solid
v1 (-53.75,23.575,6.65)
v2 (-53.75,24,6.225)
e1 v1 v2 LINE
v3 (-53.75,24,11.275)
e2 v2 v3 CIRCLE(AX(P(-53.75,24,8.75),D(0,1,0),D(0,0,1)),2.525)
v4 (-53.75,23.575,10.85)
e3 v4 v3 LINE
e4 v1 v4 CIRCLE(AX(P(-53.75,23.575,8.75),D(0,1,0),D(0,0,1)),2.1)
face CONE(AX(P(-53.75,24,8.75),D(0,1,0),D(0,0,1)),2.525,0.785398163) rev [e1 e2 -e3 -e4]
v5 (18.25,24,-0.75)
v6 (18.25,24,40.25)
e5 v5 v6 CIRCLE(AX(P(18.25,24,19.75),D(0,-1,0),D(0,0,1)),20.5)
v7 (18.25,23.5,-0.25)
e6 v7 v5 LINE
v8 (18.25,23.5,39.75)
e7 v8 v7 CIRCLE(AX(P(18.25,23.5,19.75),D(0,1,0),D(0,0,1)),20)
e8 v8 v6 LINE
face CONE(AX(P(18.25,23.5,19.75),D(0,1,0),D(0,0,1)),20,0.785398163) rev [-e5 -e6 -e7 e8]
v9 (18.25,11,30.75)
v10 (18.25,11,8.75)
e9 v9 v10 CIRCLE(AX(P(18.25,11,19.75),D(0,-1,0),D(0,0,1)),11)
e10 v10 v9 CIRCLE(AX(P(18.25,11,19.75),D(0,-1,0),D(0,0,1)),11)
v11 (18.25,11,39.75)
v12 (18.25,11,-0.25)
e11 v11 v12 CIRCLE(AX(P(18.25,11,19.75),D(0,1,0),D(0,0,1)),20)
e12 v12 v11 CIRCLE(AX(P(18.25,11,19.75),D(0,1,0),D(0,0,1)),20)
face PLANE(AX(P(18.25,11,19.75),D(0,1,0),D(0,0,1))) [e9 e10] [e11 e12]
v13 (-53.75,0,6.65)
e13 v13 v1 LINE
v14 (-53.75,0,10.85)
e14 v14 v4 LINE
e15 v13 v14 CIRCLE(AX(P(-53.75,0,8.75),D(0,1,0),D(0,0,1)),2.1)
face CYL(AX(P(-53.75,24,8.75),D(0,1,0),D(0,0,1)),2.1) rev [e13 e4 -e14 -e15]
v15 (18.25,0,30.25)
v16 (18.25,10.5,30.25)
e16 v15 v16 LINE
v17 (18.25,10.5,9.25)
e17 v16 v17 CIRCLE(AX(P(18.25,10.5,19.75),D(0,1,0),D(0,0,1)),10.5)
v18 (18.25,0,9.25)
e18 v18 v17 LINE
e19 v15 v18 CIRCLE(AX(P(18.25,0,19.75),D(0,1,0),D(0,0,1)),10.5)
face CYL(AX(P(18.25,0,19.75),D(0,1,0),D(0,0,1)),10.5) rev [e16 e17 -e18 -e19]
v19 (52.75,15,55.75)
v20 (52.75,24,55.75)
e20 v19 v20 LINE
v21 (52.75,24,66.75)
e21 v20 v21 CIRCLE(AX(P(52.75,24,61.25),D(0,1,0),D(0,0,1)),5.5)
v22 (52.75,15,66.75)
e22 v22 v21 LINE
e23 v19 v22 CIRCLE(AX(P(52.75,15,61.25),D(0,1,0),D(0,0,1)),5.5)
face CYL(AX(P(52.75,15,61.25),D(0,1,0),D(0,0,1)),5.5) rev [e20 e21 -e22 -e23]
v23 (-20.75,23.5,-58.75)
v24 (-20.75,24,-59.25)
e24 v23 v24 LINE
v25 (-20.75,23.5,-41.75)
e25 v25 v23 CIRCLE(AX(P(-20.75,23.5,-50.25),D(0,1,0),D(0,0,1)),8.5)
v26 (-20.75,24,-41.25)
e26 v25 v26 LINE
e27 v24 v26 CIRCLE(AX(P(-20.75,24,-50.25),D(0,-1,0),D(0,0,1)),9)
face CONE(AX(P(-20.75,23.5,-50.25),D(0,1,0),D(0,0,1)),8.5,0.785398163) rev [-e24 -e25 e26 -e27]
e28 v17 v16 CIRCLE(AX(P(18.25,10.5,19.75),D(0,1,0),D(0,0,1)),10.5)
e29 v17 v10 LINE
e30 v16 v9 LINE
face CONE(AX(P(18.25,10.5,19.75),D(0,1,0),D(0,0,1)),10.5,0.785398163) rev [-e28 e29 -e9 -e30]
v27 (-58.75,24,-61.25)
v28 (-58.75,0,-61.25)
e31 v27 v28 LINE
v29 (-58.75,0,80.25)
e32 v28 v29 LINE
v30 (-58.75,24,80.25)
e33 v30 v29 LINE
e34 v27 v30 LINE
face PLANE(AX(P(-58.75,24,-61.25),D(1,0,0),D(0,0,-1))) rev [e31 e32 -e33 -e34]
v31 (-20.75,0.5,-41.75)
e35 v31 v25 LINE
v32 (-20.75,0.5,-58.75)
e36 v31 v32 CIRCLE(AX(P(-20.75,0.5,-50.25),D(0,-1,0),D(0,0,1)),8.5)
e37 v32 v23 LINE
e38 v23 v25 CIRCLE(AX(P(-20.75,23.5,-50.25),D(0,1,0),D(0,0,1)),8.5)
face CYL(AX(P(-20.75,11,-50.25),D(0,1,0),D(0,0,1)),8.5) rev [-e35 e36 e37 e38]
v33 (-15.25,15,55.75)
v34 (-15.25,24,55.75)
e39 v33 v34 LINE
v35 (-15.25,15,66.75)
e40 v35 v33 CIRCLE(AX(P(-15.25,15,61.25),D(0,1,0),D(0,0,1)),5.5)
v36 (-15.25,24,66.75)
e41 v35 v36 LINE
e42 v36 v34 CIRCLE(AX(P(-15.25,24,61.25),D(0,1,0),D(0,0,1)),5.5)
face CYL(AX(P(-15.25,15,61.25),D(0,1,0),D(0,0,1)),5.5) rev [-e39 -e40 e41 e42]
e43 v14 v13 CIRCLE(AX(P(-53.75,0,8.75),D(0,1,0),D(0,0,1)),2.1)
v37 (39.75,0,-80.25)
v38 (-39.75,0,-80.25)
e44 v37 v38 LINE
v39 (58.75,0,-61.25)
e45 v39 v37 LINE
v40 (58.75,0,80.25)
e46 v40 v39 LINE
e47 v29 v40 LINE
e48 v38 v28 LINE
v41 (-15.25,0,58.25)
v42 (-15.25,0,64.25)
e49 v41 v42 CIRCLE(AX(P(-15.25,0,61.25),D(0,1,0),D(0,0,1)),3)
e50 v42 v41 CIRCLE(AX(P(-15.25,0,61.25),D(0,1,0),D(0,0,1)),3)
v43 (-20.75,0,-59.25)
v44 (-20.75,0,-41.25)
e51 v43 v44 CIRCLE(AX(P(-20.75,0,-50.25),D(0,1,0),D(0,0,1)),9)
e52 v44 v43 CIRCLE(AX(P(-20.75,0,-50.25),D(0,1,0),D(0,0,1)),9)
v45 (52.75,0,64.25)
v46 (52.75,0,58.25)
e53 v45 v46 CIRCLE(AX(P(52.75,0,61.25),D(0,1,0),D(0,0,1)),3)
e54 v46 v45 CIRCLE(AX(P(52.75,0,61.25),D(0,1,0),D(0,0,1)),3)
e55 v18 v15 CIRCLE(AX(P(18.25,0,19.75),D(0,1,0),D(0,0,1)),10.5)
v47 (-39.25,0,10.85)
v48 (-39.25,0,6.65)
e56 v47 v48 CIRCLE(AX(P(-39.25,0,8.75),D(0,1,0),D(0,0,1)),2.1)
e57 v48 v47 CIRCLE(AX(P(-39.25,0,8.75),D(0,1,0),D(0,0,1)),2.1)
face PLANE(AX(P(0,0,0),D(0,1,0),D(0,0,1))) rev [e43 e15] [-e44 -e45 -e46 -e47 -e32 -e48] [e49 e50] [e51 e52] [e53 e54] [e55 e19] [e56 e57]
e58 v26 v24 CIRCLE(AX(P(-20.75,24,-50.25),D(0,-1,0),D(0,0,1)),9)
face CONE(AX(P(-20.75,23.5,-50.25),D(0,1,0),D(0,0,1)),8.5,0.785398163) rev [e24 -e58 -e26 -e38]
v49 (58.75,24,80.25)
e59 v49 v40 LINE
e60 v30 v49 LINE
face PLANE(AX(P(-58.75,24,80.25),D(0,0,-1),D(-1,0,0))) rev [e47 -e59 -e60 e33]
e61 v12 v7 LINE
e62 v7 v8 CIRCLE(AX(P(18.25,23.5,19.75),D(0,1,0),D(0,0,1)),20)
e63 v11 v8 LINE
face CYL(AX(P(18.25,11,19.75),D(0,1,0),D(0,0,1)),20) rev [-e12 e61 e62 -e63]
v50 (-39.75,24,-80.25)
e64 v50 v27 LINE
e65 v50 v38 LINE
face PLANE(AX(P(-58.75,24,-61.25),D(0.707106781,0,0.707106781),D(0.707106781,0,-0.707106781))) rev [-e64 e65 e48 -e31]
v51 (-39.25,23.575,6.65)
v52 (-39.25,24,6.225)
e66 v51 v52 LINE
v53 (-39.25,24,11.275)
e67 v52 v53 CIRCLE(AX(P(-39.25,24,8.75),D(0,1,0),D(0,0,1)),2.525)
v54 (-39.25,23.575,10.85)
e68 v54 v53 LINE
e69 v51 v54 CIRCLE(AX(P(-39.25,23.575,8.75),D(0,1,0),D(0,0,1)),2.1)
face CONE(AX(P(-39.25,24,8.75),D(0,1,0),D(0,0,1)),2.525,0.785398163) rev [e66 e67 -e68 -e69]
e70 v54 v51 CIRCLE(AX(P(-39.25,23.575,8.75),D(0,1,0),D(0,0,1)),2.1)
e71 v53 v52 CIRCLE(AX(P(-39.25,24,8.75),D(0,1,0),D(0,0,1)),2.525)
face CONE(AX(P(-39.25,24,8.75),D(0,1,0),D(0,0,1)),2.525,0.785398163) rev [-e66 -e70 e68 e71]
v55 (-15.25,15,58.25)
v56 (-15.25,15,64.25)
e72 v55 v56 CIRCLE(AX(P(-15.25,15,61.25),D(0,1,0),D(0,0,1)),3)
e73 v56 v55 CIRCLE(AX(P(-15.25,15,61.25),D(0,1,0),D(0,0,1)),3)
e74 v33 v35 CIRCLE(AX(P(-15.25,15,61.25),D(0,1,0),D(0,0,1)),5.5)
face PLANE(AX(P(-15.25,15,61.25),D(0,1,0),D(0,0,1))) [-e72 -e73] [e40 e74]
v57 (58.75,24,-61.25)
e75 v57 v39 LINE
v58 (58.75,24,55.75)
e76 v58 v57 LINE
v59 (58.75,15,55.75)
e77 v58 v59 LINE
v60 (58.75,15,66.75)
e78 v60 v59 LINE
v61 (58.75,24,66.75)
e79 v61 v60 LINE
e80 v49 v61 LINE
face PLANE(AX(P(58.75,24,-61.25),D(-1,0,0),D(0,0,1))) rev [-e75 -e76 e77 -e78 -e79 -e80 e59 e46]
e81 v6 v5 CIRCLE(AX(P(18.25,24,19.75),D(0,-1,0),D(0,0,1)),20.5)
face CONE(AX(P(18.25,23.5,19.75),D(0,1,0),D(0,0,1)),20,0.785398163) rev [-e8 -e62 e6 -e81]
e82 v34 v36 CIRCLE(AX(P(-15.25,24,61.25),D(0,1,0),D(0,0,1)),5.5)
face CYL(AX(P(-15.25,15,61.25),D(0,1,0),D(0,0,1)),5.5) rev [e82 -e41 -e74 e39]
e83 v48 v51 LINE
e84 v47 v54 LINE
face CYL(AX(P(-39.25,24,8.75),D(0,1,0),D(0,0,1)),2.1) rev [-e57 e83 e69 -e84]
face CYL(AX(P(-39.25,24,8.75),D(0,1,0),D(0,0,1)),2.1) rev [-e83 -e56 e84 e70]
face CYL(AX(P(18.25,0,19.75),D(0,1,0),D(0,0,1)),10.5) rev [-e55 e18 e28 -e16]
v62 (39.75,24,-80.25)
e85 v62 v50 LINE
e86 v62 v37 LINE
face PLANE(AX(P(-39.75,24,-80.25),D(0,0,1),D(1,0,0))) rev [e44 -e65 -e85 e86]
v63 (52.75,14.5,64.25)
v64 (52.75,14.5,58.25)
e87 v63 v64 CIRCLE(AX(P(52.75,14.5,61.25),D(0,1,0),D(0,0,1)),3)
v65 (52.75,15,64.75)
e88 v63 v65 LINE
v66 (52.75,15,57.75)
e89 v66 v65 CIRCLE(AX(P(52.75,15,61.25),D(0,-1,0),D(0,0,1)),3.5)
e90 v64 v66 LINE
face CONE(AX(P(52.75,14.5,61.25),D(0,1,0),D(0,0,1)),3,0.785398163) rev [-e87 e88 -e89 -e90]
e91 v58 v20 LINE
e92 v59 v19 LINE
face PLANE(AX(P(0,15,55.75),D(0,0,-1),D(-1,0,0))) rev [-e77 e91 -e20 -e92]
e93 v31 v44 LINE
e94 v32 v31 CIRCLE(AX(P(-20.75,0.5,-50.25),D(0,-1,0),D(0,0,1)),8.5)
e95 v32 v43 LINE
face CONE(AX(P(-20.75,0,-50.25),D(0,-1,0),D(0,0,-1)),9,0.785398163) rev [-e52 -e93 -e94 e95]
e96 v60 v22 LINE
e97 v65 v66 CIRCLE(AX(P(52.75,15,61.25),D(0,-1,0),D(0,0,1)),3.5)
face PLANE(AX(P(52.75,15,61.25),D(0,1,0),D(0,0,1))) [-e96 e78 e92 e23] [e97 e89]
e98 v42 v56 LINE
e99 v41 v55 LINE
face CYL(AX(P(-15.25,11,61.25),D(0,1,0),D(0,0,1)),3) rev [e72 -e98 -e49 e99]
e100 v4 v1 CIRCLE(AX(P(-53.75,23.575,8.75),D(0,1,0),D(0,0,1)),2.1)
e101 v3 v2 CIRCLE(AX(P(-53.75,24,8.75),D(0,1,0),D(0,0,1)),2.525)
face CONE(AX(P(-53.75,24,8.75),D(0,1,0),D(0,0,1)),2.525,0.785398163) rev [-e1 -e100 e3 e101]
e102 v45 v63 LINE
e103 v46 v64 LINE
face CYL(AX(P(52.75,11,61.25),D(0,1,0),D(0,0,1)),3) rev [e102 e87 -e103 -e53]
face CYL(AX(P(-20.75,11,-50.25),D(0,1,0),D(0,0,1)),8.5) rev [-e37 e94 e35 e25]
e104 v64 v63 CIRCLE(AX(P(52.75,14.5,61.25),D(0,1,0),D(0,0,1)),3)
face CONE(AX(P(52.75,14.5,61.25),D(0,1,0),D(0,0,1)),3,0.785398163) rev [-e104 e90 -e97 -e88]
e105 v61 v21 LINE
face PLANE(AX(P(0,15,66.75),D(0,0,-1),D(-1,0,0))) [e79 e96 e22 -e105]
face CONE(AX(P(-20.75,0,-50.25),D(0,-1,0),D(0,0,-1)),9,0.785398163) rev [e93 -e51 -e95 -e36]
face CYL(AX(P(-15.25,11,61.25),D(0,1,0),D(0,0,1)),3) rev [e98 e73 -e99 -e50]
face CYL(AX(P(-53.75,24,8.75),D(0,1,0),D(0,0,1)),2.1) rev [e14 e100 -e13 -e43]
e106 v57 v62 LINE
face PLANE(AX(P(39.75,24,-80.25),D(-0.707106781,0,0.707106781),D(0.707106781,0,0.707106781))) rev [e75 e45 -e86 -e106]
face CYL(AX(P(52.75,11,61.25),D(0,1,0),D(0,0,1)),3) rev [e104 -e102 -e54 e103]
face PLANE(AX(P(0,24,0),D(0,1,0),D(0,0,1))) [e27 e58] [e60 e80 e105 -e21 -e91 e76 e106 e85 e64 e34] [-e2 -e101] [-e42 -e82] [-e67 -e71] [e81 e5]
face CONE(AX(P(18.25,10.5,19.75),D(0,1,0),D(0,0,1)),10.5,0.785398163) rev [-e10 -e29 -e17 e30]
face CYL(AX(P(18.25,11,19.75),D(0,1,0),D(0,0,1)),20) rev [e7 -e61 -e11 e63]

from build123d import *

# Parameters (mm, degrees)
BOSS_EXTRUDE1_DEPTH         = 24
SKETCH_2_2_R                = 8.5
SKETCH_2_2_R_2              = 20
SKETCH_2_2_R_3              = 3
CUT_EXTRUDE1_DEPTH          = 13
SKETCH_2_2_2_R              = 8.5
SKETCH_2_2_2_R_2            = 3
CUT_EXTRUDE2_DEPTH          = 103.311411876
SKETCH3_R                   = 10.5
CUT_EXTRUDE3_DEPTH          = 101.302666964
M5_TAPPED_HOLE1_D           = 4.2
M5_TAPPED_HOLE1_CSINK_D     = 5.05
M5_TAPPED_HOLE1_CSINK_ANGLE = 90
CHAMFER1_SIZE               = 0.5
CUT_EXTRUDE4_START          = -24
SKETCH6_R                   = 5.5
SKETCH6_R_2                 = 3
SKETCH6_W                   = 5.693229178
SKETCH6_H                   = 11
CUT_EXTRUDE4_DEPTH          = 9
CHAMFER2_SIZE               = 0.5


with BuildPart() as part:
    # Sketch1 → Boss-Extrude1 (new body)
    with BuildSketch(Plane(origin=(0, 0, 0), x_dir=(1, 0, 0), z_dir=(0, 1, 0))):
        Polygon((-58.75, 61.25), (-39.75, 80.25), (39.75, 80.25), (58.75, 61.25), (58.75, -80.25), (-58.75, -80.25), align=None)
    extrude(amount=BOSS_EXTRUDE1_DEPTH)

    # Sketch 2_2 → Cut-Extrude1 (cut)
    with BuildSketch(Plane(origin=(0, 24, 0), x_dir=(1, 0, 0), z_dir=(0, 1, 0))):
        with Locations(Location((-20.75, 50.25, 0), (0, 0, 270))):
            Circle(SKETCH_2_2_R)
        with Locations(Location((18.25, -19.75, 0), (0, 0, 270))):
            Circle(SKETCH_2_2_R_2)
        with Locations(Location((52.75, -61.25, 0), (0, 0, 270))):
            Circle(SKETCH_2_2_R_3)
        with Locations(Location((-15.25, -61.25, 0), (0, 0, 270))):
            Circle(SKETCH_2_2_R_3)
    extrude(amount=-CUT_EXTRUDE1_DEPTH, mode=Mode.SUBTRACT)

    # Sketch 2_2 2 → Cut-Extrude2 (cut, through all)
    with BuildSketch(Plane(origin=(0, 24, 0), x_dir=(1, 0, 0), z_dir=(0, 1, 0))):
        with Locations(Location((-20.75, 50.25, 0), (0, 0, 270))):
            Circle(SKETCH_2_2_2_R)
        with Locations(Location((52.75, -61.25, 0), (0, 0, 270))):
            Circle(SKETCH_2_2_2_R_2)
        with Locations(Location((-15.25, -61.25, 0), (0, 0, 270))):
            Circle(SKETCH_2_2_2_R_2)
    extrude(amount=-CUT_EXTRUDE2_DEPTH, mode=Mode.SUBTRACT)

    # Sketch3 → Cut-Extrude3 (cut, through all)
    with BuildSketch(Plane(origin=(0, 11, 0), x_dir=(1, 0, 0), z_dir=(0, 1, 0))):
        with Locations(Location((18.25, -19.75, 0), (0, 0, 270))):
            Circle(SKETCH3_R)
    extrude(amount=-CUT_EXTRUDE3_DEPTH, mode=Mode.SUBTRACT)

    # M5 Tapped Hole1 (through all)
    with Locations(Plane(origin=(0, 24, 0), x_dir=(1, 0, 0), z_dir=(0, 1, 0))):
        with Locations((-39.25, -8.75), (-53.75, -8.75)):
            CounterSinkHole(M5_TAPPED_HOLE1_D / 2, M5_TAPPED_HOLE1_CSINK_D / 2, counter_sink_angle=M5_TAPPED_HOLE1_CSINK_ANGLE)

    # Chamfer1
    chamfer1_edges = [part.edges().sort_by_distance(p)[0] for p in [
        (-20.75, 24, -58.75),
        (18.25, 24, -0.25),
        (-20.75, 0, -58.75),
        (18.25, 11, 9.25),
    ]]
    chamfer(chamfer1_edges, length=CHAMFER1_SIZE)

    # Sketch6 → Cut-Extrude4 (cut)
    # profile 1 of 7: a face of its own
    with BuildSketch(Plane.XZ.offset(CUT_EXTRUDE4_START)):
        with Locations(Location((-15.25, 61.25, 0), (0, 0, 90))):
            Circle(SKETCH6_R)
        with Locations(Location((-15.25, 61.25, 0), (0, 0, 90))):
            Circle(SKETCH6_R_2, mode=Mode.SUBTRACT)
    # profile 2 of 7: a face of its own
    with BuildSketch(Plane.XZ.offset(CUT_EXTRUDE4_START)):
        with BuildLine():
            ThreePointArc((58.25, 61.25), (56.639087297, 65.139087297), (52.75, 66.75))
            ThreePointArc((52.75, 66.75), (52.40269227, 66.73902335), (52.056770822, 66.706137215))
            Line((52.056770822, 66.706137215), (52.056770822, 64.168806829))
            ThreePointArc((52.056770822, 64.168806829), (54.610149519, 63.603687271), (55.75, 61.25))
            ThreePointArc((55.75, 61.25), (54.610149519, 58.896312729), (52.056770822, 58.331193171))
            Line((52.056770822, 58.331193171), (52.056770822, 55.793862785))
            ThreePointArc((52.056770822, 55.793862785), (52.40269227, 55.76097665), (52.75, 55.75))
            ThreePointArc((52.75, 55.75), (56.639087297, 57.360912703), (58.25, 61.25))
        make_face()
    # profile 3 of 7: a face of its own
    with BuildSketch(Plane.XZ.offset(CUT_EXTRUDE4_START)):
        with BuildLine():
            Line((52.056770822, 64.168806829), (52.056770822, 66.706137215))
            ThreePointArc((52.056770822, 66.706137215), (47.25, 61.25), (52.056770822, 55.793862785))
            Line((52.056770822, 55.793862785), (52.056770822, 58.331193171))
            ThreePointArc((52.056770822, 58.331193171), (49.75, 61.25), (52.056770822, 64.168806829))
        make_face()
    # profile 4 of 7: a face of its own
    with BuildSketch(Plane.XZ.offset(CUT_EXTRUDE4_START)):
        with Locations((61.596614589, 61.25)):
            Rectangle(SKETCH6_W, SKETCH6_H)
    # profile 5 of 7: a face of its own
    with BuildSketch(Plane.XZ.offset(CUT_EXTRUDE4_START)):
        with BuildLine():
            ThreePointArc((58.25, 61.25), (56.639087297, 65.139087297), (52.75, 66.75))
            ThreePointArc((52.75, 66.75), (52.40269227, 66.73902335), (52.056770822, 66.706137215))
            Line((52.056770822, 66.706137215), (52.056770822, 64.168806829))
            ThreePointArc((52.056770822, 64.168806829), (54.610149519, 63.603687271), (55.75, 61.25))
            ThreePointArc((55.75, 61.25), (54.610149519, 58.896312729), (52.056770822, 58.331193171))
            Line((52.056770822, 58.331193171), (52.056770822, 55.793862785))
            ThreePointArc((52.056770822, 55.793862785), (52.40269227, 55.76097665), (52.75, 55.75))
            ThreePointArc((52.75, 55.75), (56.639087297, 57.360912703), (58.25, 61.25))
        make_face()
    # profile 6 of 7: a face of its own
    with BuildSketch(Plane.XZ.offset(CUT_EXTRUDE4_START)):
        with BuildLine():
            Line((52.056770822, 64.168806829), (52.056770822, 66.706137215))
            ThreePointArc((52.056770822, 66.706137215), (47.25, 61.25), (52.056770822, 55.793862785))
            Line((52.056770822, 55.793862785), (52.056770822, 58.331193171))
            ThreePointArc((52.056770822, 58.331193171), (49.75, 61.25), (52.056770822, 64.168806829))
        make_face()
    # profile 7 of 7: a face of its own
    with BuildSketch(Plane.XZ.offset(CUT_EXTRUDE4_START)):
        with BuildLine():
            Line((58.75, 66.75), (52.75, 66.75))
            ThreePointArc((52.75, 66.75), (56.639087297, 65.139087297), (58.25, 61.25))
            ThreePointArc((58.25, 61.25), (56.639087297, 57.360912703), (52.75, 55.75))
            Line((52.75, 55.75), (58.75, 55.75))
            Line((58.75, 55.75), (58.75, 66.75))
        make_face()
    extrude(amount=CUT_EXTRUDE4_DEPTH, mode=Mode.SUBTRACT)

    # Chamfer2
    chamfer2_edges = [part.edges().sort_by_distance(p)[0] for p in [
        (52.75, 15, 58.25),
    ]]
    chamfer(chamfer2_edges, length=CHAMFER2_SIZE)


solid = part.part
